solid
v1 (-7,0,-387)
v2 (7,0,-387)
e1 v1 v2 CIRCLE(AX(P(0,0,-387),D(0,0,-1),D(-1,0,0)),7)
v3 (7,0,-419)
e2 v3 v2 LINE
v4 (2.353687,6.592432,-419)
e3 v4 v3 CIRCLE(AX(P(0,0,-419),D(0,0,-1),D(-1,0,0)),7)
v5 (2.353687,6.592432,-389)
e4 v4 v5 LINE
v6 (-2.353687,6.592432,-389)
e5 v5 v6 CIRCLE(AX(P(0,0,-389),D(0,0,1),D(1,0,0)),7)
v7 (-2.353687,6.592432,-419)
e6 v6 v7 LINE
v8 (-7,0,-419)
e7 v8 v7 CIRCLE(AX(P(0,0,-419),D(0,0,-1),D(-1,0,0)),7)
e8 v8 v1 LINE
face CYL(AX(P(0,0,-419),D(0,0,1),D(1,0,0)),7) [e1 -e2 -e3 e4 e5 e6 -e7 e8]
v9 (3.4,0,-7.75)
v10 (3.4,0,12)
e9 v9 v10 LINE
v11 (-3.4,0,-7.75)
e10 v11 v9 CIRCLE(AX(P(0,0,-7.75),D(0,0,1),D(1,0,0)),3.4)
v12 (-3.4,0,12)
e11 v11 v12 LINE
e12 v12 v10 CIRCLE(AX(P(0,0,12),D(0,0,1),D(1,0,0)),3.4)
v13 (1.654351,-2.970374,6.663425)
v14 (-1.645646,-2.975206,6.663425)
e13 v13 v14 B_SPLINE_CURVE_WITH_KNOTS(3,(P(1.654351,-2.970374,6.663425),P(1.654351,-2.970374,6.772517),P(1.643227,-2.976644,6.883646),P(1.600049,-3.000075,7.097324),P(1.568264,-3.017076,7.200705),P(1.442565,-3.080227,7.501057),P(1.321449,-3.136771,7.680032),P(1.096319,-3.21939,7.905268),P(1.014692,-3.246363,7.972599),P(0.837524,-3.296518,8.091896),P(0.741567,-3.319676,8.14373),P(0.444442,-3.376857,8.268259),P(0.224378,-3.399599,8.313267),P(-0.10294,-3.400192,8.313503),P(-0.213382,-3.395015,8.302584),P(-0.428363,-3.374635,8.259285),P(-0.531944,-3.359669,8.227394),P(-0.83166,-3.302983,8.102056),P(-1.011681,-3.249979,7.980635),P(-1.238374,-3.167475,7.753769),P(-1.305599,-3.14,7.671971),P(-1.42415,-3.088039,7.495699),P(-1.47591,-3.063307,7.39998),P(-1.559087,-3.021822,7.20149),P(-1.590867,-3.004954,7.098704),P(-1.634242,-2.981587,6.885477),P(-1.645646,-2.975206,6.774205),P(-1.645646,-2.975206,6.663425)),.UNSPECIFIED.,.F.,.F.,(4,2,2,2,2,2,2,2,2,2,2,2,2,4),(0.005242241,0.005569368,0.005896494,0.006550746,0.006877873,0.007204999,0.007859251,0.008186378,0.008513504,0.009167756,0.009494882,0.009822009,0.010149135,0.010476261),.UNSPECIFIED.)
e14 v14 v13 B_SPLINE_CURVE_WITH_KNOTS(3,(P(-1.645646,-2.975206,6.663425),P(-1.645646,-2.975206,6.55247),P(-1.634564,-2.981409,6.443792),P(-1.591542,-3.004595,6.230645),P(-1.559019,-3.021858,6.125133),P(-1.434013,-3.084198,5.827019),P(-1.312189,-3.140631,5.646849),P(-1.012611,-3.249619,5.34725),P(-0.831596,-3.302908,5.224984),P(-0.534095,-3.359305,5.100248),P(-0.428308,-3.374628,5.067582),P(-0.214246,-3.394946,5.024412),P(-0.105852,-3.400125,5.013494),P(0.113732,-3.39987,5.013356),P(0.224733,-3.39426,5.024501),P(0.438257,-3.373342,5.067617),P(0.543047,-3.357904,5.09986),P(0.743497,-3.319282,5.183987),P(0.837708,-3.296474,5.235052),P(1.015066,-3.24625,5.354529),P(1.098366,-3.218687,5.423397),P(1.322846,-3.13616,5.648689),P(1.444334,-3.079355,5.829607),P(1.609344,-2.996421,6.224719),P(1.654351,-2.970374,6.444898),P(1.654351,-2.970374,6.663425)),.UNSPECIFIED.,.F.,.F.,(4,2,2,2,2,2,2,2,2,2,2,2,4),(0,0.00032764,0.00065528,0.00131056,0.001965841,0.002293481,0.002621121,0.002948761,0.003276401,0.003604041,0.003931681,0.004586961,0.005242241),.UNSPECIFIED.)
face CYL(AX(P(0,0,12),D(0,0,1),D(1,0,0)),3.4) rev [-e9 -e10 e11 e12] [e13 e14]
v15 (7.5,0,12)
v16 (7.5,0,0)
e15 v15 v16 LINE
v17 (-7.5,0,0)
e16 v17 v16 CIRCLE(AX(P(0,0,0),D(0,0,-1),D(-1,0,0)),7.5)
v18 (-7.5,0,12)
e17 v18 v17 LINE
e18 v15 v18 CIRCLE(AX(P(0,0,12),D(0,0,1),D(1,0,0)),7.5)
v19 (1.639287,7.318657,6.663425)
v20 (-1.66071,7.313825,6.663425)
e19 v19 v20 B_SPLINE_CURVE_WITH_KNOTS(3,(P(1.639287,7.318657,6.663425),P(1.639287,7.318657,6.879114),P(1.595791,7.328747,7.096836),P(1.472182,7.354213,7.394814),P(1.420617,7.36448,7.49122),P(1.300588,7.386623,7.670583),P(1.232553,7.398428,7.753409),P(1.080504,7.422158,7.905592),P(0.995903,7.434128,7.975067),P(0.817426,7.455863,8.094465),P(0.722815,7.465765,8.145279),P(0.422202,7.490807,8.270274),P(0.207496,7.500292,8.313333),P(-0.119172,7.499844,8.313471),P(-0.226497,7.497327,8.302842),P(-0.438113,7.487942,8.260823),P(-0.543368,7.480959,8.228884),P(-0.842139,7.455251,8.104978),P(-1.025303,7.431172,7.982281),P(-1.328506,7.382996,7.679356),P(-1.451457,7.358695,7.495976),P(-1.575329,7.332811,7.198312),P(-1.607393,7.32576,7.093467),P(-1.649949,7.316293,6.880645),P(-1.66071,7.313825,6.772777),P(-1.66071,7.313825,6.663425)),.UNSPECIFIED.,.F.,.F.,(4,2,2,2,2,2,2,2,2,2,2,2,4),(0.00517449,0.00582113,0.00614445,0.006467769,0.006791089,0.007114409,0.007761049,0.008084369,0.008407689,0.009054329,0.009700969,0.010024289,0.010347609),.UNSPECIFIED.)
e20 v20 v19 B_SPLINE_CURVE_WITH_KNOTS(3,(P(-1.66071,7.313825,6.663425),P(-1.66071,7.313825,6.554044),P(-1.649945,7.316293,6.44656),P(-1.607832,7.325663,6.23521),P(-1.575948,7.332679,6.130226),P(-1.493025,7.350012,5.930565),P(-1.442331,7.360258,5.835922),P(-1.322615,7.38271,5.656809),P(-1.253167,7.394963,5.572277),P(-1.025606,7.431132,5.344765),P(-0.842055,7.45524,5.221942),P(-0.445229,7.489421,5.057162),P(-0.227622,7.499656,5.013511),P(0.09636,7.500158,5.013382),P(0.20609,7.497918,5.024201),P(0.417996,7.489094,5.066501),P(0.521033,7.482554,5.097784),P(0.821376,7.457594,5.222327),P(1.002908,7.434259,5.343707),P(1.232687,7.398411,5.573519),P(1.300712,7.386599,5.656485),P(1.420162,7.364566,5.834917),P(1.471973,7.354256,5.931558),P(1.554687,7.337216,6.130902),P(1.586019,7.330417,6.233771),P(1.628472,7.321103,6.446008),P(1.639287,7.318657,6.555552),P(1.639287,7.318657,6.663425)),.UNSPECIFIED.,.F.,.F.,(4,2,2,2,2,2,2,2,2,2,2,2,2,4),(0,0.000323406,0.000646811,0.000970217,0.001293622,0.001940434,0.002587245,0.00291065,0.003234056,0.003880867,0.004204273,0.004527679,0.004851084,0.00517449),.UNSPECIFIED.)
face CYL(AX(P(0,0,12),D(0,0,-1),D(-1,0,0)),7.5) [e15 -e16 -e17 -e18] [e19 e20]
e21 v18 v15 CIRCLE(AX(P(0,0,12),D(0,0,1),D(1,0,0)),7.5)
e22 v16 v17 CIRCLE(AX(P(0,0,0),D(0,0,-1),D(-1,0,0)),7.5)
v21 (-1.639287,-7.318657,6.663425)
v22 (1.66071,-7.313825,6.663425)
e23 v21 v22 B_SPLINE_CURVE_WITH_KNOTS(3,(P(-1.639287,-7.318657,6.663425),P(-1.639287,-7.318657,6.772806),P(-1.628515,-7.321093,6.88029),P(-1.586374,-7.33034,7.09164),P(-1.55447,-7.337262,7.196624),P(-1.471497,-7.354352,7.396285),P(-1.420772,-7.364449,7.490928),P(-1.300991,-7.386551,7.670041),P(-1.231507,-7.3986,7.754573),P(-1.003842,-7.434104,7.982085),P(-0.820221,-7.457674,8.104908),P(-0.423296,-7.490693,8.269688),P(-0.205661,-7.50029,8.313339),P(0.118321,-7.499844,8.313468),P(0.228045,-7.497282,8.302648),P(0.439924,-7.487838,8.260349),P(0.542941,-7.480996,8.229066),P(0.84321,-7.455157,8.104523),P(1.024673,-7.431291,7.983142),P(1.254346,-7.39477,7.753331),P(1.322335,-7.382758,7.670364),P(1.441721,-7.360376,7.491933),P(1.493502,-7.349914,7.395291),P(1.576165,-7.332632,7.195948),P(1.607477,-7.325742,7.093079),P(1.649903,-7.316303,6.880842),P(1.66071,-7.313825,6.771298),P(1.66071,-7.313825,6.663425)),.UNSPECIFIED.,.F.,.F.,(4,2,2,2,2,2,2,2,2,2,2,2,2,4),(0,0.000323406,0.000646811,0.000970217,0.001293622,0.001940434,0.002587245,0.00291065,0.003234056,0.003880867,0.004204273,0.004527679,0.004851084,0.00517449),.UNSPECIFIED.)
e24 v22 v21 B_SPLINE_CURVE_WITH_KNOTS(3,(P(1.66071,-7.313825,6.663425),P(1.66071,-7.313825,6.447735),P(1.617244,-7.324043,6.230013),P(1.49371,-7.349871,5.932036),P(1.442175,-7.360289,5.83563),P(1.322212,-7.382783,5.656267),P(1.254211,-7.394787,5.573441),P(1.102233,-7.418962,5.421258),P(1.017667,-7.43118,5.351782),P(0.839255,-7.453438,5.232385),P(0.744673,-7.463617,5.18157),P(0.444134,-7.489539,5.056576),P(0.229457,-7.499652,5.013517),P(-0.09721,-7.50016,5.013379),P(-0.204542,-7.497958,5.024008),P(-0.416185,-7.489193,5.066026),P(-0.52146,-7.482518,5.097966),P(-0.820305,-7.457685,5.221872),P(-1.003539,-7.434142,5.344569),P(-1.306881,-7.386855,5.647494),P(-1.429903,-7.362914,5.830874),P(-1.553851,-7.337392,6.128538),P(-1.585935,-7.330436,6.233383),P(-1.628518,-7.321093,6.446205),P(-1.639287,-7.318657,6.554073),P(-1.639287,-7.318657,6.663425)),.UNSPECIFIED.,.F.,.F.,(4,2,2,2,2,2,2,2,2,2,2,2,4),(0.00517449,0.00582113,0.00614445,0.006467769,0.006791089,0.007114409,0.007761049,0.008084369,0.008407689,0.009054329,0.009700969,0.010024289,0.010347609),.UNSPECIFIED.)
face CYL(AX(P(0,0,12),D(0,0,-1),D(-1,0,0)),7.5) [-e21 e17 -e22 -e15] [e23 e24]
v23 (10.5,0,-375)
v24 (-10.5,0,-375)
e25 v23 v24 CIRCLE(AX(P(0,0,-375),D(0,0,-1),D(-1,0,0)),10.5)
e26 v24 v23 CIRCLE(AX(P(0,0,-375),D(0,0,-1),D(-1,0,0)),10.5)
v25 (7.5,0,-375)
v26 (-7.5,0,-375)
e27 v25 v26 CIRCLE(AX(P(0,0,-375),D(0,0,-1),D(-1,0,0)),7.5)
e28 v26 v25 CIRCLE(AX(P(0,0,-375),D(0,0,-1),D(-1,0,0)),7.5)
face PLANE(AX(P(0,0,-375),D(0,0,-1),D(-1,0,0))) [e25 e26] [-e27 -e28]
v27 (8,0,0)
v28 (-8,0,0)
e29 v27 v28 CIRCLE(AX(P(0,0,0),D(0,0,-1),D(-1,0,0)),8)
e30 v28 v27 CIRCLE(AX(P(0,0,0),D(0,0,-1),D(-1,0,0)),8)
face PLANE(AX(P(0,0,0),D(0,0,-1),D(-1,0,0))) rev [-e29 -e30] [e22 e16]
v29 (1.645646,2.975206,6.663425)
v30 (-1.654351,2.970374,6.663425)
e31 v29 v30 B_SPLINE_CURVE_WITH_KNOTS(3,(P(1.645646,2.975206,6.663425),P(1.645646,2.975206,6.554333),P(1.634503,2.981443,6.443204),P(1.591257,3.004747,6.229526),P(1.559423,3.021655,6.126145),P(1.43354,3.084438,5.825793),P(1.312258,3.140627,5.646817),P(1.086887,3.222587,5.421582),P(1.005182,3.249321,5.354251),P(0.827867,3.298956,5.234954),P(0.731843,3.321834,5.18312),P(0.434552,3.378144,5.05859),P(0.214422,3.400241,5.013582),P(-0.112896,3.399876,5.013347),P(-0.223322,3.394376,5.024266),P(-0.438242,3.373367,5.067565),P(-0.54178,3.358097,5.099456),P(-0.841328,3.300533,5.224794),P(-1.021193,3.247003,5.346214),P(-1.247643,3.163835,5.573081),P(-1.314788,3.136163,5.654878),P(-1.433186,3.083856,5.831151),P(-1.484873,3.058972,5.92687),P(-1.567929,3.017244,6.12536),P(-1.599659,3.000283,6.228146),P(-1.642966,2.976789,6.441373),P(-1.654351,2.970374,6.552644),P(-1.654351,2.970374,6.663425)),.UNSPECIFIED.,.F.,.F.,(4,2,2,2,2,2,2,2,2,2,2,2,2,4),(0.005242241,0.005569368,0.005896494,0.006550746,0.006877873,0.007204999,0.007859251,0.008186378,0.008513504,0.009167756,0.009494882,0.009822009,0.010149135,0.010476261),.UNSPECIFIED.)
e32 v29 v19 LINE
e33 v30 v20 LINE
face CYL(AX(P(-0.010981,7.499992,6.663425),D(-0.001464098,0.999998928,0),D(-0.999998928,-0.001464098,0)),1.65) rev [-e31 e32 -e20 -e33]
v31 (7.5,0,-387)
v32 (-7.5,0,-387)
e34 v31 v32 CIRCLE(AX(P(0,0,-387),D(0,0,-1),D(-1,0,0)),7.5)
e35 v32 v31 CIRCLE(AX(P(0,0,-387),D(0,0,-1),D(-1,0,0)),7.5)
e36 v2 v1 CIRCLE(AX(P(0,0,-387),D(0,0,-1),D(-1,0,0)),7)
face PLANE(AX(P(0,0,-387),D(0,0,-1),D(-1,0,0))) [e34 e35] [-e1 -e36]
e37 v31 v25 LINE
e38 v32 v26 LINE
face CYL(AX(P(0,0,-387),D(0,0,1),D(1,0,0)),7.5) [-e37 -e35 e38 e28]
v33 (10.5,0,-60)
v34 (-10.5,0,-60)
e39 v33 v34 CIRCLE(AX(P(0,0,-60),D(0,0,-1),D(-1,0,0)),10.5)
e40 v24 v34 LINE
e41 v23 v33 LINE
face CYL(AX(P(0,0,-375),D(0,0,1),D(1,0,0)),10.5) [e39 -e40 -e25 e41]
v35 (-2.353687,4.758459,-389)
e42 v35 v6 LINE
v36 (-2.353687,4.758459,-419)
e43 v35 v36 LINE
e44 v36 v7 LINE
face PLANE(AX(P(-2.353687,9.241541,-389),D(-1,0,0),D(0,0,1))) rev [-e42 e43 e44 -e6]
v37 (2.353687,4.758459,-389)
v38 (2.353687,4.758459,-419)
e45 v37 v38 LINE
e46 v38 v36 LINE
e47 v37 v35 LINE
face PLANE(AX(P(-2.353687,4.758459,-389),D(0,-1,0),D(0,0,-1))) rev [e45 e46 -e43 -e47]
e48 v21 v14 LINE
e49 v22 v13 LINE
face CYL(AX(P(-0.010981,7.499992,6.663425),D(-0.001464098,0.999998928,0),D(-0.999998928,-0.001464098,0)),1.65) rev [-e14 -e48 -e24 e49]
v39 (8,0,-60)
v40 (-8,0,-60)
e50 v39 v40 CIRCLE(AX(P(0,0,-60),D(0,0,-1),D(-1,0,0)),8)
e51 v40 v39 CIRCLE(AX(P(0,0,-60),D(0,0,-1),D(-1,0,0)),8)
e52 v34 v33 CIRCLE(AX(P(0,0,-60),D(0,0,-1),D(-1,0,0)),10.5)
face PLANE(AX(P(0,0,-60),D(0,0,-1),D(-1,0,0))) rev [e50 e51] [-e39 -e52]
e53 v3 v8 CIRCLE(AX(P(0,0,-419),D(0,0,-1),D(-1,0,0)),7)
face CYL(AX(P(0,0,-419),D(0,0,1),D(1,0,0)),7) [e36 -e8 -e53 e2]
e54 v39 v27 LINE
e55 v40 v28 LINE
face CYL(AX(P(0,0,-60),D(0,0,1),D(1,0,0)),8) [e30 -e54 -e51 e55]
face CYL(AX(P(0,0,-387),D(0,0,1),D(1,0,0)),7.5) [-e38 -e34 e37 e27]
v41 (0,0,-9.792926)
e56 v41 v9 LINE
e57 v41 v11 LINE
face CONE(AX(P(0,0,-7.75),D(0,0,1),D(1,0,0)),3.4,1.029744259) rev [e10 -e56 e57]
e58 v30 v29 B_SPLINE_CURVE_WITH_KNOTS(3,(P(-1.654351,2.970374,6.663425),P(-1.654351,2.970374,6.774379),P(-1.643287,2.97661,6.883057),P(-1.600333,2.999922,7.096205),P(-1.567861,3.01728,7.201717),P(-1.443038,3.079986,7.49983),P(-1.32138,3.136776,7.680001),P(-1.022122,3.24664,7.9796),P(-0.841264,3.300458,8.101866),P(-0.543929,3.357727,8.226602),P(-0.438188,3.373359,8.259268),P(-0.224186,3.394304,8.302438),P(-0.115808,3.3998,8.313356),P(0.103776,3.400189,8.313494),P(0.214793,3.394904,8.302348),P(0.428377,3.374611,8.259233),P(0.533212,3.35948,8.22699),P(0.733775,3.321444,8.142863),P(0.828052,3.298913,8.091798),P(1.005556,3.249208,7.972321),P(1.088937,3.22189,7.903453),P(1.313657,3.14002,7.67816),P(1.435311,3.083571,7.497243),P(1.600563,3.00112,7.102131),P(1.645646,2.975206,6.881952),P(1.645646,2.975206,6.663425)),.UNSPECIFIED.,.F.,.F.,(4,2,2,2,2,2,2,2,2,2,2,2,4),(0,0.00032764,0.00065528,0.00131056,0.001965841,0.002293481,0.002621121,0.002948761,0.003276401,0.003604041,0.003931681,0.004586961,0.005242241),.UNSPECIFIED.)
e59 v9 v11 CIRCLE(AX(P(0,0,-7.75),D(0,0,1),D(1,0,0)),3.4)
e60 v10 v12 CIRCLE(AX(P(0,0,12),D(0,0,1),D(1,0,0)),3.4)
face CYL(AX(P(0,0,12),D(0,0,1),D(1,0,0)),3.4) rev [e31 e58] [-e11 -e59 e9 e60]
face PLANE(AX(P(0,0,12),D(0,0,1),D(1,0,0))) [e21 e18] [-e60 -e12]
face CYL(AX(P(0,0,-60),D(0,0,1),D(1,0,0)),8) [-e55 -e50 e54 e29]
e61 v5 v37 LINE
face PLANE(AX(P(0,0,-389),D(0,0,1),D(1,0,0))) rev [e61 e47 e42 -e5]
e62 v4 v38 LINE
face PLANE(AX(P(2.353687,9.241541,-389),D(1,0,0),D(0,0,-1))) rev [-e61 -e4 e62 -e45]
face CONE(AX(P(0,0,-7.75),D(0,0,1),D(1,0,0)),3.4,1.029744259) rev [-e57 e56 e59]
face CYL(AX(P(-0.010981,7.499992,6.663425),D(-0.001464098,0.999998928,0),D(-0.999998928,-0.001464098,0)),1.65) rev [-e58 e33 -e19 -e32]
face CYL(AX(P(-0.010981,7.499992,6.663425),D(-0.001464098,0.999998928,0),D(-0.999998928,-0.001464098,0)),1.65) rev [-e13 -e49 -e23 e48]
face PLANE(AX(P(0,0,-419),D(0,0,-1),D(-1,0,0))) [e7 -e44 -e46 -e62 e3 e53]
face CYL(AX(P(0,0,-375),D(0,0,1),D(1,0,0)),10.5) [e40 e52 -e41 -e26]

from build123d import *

# Parameters (mm, degrees)
SKETCH_1_R             = 7.5
EXTRUDE_1_DEPTH        = 12
SKETCH_2_R             = 8
EXTRUDE_2_DEPTH        = 60
SKETCH_3_R             = 10.5
EXTRUDE_3_DEPTH        = 315
EXTRUDE_START          = 12
SKETCH_4_R             = 7.5
EXTRUDE_4_DEPTH        = 12
SKETCH_5_R             = 7
EXTRUDE_5_DEPTH        = 32
SKETCH_6_W             = 4.707373346
SKETCH_6_H             = 4.483082856
CUT_EXTRUDE_1_DEPTH    = 30
HOLE_WIZARD_M8_1_D     = 6.8
HOLE_WIZARD_M8_1_DEPTH = 19.75
HOLE_WIZARD_M8_1_TIP   = 2.042926105
HOLE_WIZARD_M4_1_D     = 3.3


with BuildPart() as part:
    # 草图1 → 凸台-拉伸1 (new body)
    with BuildSketch(Plane.XY):
        Circle(SKETCH_1_R)
    extrude(amount=EXTRUDE_1_DEPTH)

    # 草图2 → 凸台-拉伸2 (add)
    with BuildSketch(Plane(origin=(0, 0, 0), x_dir=(-1, 0, 0), z_dir=(0, 0, -1))):
        Circle(SKETCH_2_R)
    extrude(amount=EXTRUDE_2_DEPTH)

    # 草图3 → 凸台-拉伸3 (add)
    with BuildSketch(Plane(origin=(0, 0, -60), x_dir=(-1, 0, 0), z_dir=(0, 0, -1))):
        Circle(SKETCH_3_R)
    extrude(amount=EXTRUDE_3_DEPTH)

    # 草图4 → 凸台-拉伸4 (add)
    with BuildSketch(Plane(origin=(0, 0, -375), x_dir=(-1, 0, 0), z_dir=(0, 0, -1)).offset(EXTRUDE_START)):
        Circle(SKETCH_4_R)
    extrude(amount=-EXTRUDE_4_DEPTH)

    # 草图5 → 凸台-拉伸5 (add)
    with BuildSketch(Plane(origin=(0, 0, -387), x_dir=(-1, 0, 0), z_dir=(0, 0, -1))):
        Circle(SKETCH_5_R)
    extrude(amount=EXTRUDE_5_DEPTH)

    # 草图6 → 切除-拉伸1 (cut)
    with BuildSketch(Plane(origin=(0, 0, -419), x_dir=(-1, 0, 0), z_dir=(0, 0, -1))):
        with Locations((0, 7)):
            Rectangle(SKETCH_6_W, SKETCH_6_H)
    extrude(amount=-CUT_EXTRUDE_1_DEPTH, mode=Mode.SUBTRACT)

    # M8 螺纹孔1
    with Locations(Plane.XY.offset(12)):
        with Locations((0, 0)):
            Hole(HOLE_WIZARD_M8_1_D / 2, depth=HOLE_WIZARD_M8_1_DEPTH)
            with Locations((0, 0, -(HOLE_WIZARD_M8_1_DEPTH + HOLE_WIZARD_M8_1_TIP / 2))):  # 118° drill point
                Cone(0, HOLE_WIZARD_M8_1_D / 2, HOLE_WIZARD_M8_1_TIP, mode=Mode.SUBTRACT)

    # M4 螺纹孔1 (through all)
    with Locations(Plane(origin=(-0.010980736, 7.499991962, 6.6634249), x_dir=(0.999998928208, 0.001464098146, 0), z_dir=(-0.001464098146, 0.999998928208, 0))):
        with Locations((0, 0)):
            Hole(HOLE_WIZARD_M4_1_D / 2)


solid = part.part
